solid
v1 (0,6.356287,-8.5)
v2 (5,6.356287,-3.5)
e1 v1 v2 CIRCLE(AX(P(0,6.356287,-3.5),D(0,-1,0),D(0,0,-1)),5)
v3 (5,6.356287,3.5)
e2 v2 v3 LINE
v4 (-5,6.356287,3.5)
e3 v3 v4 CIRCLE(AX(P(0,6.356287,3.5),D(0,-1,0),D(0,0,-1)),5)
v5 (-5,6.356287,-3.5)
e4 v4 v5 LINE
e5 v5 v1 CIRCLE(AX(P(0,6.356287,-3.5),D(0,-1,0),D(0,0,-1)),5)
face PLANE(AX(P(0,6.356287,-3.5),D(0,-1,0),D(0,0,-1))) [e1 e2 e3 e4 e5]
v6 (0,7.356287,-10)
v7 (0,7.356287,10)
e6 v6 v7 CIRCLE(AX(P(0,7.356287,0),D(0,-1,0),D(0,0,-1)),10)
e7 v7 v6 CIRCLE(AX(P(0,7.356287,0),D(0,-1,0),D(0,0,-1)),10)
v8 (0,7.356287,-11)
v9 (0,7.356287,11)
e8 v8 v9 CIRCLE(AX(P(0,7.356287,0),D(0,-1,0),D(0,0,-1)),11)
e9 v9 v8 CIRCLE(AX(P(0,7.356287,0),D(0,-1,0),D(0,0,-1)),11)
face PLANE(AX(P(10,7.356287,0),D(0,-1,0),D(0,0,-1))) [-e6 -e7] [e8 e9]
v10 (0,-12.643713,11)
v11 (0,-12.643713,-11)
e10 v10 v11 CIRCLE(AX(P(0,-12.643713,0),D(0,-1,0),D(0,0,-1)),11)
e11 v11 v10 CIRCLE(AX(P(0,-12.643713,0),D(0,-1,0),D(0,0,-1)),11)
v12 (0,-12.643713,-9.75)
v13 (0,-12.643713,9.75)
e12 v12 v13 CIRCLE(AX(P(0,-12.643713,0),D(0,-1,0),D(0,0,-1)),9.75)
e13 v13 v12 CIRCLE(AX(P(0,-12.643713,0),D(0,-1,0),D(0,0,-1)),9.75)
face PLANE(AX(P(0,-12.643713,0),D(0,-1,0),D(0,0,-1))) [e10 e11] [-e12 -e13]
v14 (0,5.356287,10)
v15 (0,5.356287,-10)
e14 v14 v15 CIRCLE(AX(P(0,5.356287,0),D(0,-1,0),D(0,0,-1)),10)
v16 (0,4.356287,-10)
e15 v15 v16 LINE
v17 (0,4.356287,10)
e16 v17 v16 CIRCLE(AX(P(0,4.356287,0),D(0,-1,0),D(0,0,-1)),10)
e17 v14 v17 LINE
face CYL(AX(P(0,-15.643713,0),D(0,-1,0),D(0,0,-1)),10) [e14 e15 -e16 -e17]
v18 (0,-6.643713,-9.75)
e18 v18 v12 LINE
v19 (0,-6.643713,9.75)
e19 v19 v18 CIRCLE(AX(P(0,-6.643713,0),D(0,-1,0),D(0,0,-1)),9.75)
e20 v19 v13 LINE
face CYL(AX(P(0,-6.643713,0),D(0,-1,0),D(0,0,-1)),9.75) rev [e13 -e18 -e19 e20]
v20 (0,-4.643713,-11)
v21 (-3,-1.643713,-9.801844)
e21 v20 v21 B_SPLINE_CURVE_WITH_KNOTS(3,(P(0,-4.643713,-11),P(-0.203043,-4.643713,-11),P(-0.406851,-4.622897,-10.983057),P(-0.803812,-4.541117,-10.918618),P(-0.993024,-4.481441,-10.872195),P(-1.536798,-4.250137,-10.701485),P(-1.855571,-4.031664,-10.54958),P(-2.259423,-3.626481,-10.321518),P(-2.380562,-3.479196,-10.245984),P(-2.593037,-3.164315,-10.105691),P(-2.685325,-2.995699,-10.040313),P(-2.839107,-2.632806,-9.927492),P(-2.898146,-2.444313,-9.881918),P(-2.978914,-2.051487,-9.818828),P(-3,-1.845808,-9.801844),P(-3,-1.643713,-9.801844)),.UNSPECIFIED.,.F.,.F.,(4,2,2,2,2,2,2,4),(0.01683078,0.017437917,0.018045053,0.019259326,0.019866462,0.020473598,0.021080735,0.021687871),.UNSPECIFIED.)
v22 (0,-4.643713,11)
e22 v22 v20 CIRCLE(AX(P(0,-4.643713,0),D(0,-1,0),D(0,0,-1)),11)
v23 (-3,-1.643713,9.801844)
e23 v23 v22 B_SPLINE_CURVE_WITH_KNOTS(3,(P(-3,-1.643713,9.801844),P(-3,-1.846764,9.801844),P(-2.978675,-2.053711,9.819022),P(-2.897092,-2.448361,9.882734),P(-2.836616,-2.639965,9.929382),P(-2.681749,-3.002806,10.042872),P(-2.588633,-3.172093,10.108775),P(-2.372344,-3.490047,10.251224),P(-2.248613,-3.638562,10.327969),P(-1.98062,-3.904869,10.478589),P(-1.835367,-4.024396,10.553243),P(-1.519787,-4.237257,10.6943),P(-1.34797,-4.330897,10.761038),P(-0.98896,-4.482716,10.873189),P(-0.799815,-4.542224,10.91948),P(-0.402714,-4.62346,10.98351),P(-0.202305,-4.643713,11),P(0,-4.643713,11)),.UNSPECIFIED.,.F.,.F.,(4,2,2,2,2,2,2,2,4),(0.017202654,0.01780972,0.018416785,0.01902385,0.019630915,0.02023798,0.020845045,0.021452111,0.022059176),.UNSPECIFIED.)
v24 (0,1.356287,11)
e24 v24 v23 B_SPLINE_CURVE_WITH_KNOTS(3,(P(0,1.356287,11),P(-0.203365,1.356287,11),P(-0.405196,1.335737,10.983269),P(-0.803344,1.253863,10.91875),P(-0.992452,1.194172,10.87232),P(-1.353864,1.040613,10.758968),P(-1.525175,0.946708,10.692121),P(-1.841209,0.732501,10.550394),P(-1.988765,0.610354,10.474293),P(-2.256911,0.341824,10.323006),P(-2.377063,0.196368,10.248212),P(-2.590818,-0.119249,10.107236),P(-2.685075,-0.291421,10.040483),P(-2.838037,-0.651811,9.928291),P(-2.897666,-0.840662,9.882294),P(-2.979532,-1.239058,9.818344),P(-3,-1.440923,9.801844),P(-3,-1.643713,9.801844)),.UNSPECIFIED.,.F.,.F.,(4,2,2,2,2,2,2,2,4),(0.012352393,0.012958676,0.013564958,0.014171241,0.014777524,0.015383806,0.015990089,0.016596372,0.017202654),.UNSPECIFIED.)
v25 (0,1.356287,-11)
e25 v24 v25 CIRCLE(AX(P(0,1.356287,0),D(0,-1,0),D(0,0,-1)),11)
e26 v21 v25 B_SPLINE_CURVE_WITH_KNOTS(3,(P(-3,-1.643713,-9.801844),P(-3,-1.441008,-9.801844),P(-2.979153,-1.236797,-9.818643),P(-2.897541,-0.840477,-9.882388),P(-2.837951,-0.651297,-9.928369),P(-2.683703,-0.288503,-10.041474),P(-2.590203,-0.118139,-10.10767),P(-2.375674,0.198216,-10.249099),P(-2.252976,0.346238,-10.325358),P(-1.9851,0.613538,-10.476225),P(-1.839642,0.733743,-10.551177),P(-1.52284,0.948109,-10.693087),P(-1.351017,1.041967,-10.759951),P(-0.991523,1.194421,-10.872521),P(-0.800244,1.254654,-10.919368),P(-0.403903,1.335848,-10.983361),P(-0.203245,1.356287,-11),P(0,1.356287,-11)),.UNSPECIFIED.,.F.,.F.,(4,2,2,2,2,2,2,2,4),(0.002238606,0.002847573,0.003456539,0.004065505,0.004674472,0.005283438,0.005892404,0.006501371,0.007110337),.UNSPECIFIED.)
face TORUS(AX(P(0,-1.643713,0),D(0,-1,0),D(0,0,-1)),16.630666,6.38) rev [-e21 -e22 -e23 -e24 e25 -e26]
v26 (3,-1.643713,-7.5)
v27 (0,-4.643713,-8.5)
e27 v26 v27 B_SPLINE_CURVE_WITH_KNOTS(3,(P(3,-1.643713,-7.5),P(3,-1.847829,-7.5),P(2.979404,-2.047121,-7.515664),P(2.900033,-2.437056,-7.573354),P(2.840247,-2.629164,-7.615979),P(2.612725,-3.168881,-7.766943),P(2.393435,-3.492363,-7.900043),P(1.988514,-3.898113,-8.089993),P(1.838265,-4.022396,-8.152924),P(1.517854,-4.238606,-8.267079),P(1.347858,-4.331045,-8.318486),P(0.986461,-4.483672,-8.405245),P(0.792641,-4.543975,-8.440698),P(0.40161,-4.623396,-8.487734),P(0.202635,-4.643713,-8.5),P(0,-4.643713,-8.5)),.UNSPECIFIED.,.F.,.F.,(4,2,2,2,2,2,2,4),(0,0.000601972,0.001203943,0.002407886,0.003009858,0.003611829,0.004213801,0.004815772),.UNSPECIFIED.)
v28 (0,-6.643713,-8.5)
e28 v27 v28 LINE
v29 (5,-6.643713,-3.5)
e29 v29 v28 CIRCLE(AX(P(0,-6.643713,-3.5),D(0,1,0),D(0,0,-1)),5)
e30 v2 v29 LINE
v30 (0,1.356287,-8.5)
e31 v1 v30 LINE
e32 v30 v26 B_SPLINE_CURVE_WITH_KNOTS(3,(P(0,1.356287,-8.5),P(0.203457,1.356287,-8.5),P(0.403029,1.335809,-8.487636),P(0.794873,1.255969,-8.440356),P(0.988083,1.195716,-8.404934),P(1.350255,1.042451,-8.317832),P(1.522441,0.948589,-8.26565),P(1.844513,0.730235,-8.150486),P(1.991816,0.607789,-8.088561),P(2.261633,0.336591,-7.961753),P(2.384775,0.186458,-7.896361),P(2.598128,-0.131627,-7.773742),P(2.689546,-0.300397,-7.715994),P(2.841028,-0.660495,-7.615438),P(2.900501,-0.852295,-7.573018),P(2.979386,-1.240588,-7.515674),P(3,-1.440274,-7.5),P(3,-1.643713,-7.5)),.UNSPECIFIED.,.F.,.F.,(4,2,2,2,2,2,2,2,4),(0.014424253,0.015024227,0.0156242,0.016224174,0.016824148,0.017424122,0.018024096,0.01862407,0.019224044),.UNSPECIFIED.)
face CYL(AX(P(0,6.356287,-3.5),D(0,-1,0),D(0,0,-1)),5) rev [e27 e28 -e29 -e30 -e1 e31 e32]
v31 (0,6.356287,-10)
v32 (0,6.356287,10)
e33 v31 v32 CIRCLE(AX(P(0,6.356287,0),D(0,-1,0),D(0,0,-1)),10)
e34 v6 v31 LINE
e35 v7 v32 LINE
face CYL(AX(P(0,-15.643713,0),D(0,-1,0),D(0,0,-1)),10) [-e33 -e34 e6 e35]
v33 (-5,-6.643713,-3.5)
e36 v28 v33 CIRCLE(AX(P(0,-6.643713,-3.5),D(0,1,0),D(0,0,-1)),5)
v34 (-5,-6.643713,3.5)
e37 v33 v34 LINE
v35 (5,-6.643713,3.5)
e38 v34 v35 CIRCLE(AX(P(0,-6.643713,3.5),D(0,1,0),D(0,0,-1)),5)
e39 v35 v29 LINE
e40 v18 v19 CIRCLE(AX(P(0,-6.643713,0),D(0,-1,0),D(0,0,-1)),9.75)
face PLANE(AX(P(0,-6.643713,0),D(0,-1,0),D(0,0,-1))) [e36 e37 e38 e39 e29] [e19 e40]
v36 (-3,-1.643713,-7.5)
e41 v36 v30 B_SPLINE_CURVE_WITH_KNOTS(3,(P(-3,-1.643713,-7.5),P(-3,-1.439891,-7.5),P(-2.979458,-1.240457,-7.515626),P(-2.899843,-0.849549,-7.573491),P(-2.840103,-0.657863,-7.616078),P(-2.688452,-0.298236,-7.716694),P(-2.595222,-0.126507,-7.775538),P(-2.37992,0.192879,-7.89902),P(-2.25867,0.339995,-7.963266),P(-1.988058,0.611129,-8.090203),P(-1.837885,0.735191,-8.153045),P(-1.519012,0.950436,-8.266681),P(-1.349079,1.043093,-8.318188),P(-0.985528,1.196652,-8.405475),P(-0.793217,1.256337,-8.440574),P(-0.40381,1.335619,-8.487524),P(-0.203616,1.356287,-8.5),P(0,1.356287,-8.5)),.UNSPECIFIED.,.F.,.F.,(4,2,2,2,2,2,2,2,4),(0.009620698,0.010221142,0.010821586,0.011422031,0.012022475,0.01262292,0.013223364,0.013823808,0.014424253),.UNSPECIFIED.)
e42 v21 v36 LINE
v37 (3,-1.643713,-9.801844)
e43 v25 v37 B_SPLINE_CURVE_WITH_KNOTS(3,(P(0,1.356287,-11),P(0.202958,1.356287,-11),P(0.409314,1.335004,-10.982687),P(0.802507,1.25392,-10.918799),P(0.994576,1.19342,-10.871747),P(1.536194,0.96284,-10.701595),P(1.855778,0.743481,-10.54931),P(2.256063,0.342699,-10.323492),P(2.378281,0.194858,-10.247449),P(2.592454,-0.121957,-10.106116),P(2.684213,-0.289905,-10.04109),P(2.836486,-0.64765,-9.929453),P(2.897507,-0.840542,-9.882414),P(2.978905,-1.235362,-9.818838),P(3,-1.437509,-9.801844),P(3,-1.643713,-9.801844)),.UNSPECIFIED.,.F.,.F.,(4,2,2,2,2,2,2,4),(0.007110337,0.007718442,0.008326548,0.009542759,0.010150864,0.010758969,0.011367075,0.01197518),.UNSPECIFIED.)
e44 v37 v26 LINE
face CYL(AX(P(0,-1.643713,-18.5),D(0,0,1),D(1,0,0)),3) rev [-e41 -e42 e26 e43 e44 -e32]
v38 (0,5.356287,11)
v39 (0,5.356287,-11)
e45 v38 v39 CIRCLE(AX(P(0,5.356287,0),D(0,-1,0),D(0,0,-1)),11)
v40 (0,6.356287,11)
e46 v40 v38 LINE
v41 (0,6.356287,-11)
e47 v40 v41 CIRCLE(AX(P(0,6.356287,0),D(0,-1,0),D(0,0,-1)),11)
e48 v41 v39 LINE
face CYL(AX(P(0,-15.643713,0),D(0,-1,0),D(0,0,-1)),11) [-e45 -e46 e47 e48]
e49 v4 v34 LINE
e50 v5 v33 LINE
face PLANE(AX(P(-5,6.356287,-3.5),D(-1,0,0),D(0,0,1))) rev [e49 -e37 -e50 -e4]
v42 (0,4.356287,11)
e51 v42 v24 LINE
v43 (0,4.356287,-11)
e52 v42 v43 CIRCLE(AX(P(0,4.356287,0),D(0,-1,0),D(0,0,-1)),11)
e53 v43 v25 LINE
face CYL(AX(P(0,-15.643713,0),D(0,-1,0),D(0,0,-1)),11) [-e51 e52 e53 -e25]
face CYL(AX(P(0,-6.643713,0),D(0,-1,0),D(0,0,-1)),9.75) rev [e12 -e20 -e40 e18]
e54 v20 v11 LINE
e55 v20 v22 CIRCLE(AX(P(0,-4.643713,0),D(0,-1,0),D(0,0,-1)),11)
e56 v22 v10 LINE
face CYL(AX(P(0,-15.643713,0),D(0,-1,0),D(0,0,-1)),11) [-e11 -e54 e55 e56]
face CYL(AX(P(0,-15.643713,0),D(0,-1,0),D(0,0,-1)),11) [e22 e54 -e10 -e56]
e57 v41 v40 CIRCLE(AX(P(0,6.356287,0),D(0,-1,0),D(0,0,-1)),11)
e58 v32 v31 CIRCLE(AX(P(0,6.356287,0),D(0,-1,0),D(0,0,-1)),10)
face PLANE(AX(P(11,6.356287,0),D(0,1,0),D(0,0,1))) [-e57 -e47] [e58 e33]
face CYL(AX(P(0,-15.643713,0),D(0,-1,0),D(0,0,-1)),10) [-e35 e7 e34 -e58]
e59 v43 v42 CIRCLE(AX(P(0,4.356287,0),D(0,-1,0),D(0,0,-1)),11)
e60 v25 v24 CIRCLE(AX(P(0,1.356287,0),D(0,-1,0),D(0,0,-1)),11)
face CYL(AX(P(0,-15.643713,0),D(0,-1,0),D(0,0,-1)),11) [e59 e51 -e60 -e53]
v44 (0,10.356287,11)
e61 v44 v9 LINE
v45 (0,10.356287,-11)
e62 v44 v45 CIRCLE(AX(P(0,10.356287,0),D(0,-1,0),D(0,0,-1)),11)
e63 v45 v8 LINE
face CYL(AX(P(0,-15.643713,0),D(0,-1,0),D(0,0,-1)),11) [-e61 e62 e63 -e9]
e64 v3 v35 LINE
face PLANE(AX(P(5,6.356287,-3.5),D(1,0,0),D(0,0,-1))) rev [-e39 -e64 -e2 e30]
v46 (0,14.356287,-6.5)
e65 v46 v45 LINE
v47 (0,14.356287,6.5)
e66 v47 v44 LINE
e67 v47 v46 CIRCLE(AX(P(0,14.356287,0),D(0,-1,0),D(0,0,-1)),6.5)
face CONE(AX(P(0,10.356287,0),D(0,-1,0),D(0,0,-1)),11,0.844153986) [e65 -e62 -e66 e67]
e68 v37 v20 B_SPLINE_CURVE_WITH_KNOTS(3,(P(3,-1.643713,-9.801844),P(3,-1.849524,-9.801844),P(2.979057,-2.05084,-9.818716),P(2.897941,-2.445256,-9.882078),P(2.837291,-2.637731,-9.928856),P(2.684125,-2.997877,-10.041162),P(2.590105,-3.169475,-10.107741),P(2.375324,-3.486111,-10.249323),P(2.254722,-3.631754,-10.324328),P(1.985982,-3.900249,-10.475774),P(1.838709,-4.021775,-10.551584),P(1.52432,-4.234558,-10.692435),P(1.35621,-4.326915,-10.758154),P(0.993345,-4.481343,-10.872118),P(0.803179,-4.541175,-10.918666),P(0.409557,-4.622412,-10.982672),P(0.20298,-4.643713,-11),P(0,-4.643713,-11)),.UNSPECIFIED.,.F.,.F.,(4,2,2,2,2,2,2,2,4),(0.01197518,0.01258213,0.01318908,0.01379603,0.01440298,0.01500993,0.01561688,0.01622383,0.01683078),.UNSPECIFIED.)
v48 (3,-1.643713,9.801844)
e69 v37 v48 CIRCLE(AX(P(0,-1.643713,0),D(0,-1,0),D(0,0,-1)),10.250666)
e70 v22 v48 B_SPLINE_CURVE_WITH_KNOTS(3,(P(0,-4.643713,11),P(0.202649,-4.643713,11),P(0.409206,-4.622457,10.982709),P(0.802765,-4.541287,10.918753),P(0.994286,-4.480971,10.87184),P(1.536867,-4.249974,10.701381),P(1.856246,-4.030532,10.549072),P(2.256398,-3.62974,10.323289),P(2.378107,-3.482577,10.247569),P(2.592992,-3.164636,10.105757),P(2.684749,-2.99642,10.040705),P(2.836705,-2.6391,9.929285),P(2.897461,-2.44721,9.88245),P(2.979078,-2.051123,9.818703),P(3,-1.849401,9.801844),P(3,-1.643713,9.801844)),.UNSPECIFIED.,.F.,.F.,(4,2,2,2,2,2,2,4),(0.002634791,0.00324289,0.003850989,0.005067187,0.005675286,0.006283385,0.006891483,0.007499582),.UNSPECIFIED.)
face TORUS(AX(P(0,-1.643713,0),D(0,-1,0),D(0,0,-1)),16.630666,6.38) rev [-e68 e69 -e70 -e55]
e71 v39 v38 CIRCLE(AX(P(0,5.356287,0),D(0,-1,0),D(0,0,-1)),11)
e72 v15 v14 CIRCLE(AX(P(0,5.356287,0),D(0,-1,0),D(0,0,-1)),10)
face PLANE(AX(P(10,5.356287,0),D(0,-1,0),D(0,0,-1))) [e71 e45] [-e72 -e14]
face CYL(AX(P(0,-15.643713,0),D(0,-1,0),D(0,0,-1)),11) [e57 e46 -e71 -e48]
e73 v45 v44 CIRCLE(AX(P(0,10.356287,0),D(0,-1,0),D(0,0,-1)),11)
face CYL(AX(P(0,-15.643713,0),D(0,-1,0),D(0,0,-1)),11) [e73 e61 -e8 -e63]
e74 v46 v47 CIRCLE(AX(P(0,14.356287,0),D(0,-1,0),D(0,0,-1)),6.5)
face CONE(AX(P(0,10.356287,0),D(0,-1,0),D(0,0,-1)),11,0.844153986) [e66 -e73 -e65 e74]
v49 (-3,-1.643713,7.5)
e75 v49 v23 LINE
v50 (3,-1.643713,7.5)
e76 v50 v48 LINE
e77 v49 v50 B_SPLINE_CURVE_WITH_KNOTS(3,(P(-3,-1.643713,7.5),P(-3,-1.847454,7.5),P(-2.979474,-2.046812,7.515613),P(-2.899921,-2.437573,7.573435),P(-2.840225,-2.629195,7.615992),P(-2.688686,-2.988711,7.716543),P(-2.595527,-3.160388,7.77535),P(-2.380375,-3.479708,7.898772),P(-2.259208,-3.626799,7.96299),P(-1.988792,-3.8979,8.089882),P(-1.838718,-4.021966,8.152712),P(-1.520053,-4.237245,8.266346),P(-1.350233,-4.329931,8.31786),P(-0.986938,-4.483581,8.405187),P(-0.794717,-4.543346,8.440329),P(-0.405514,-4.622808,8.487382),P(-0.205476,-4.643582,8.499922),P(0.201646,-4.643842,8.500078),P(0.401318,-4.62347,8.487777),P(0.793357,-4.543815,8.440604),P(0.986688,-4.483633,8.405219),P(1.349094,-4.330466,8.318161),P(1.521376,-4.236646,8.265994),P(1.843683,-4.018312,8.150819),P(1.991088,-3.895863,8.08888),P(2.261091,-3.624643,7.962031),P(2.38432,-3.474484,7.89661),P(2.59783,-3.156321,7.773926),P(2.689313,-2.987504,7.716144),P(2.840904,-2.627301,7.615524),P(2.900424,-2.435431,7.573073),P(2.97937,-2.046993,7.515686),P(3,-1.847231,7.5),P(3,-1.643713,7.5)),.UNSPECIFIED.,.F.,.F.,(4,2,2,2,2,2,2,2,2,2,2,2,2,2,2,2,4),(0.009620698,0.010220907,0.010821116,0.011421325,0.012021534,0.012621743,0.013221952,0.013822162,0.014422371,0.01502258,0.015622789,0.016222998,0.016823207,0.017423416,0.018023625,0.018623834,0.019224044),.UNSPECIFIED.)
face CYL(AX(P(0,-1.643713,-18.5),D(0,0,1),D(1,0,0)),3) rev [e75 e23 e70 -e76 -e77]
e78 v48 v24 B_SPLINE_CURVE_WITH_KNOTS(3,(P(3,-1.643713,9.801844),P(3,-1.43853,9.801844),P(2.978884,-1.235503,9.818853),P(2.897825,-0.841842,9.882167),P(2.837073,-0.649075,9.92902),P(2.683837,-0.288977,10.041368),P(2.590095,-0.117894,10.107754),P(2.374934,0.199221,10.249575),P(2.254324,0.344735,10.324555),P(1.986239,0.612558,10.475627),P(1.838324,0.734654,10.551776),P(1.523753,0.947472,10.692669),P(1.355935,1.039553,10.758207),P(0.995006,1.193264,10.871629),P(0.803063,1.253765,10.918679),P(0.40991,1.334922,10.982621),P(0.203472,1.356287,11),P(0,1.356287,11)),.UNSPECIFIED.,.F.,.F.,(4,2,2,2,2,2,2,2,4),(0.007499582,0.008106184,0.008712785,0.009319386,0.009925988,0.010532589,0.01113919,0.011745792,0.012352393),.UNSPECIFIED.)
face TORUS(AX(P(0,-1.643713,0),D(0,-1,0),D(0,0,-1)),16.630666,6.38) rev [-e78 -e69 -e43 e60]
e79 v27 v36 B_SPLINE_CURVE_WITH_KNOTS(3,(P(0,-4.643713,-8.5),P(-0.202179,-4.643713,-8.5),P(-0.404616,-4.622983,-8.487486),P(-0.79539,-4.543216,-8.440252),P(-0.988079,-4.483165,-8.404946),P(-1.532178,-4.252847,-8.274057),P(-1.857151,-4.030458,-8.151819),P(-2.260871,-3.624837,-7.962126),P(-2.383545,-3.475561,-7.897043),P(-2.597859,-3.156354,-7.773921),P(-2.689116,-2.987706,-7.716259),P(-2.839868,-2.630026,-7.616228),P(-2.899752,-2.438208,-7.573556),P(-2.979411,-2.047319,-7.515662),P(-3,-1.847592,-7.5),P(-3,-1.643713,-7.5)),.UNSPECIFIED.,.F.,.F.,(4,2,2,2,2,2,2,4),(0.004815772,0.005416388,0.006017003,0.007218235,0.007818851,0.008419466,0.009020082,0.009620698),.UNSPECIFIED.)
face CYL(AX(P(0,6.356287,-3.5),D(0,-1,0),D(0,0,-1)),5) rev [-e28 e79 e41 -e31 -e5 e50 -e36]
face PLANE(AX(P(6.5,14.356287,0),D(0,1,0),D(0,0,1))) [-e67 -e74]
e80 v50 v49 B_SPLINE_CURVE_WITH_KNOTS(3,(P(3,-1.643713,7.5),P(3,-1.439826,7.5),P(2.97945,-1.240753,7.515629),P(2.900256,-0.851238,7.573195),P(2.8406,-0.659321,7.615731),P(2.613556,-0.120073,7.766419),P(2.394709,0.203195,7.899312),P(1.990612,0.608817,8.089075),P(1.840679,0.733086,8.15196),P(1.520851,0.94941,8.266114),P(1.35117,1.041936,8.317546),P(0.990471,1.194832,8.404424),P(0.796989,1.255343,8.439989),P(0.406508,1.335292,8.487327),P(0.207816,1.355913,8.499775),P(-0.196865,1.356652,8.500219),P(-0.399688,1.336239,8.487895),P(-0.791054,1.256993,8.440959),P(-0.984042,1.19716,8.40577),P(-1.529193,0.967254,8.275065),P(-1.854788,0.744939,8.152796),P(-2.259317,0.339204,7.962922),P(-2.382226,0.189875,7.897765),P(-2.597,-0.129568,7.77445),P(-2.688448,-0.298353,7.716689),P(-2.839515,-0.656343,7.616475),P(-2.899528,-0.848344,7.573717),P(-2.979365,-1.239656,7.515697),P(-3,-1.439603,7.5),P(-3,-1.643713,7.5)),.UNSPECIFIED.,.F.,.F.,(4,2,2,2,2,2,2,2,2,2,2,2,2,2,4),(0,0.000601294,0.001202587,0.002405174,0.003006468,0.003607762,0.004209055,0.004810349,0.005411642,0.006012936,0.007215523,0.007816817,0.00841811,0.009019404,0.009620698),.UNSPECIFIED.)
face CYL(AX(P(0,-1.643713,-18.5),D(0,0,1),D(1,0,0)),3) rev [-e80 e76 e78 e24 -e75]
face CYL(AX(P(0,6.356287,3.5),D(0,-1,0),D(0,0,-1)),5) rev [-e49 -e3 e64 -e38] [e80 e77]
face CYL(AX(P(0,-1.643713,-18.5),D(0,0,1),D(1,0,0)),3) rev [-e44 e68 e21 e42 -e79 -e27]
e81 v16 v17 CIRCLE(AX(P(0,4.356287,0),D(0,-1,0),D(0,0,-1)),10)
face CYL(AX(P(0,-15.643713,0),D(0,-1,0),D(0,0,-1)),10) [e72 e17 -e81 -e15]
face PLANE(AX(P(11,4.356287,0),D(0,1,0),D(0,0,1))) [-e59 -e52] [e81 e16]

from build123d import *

# Parameters (mm, degrees)
CON_ROD_SLOT_DEPTH        = 19
UNDERSIDE_BORE_SKETCH_R   = 9.75
UNDERSIDE_BORE_19_5_DEPTH = 6
WRIST_PIN_HOLE_SKETCH_R   = 3
WRIST_PIN_HOLE_6_DEPTH    = 18.500000000000004


with BuildPart() as part:
    # Piston Profile Sketch → Piston Body (revolve)
    with BuildSketch(Plane.XY, mode=Mode.PRIVATE) as piston_body_sk:
        with BuildLine():
            Line((0, -12.6437125748503), (11.000000000000002, -12.6437125748503))
            Line((11.000000000000002, -12.6437125748503), (11.000000000000002, -4.643712574850299))
            ThreePointArc((11.000000000000002, -4.643712574850299), (10.250666035204008, -1.6437125748502983), (11.000000000000002, 1.3562874251497004))
            Line((11.000000000000002, 1.3562874251497004), (11.000000000000002, 4.356287425149702))
            Line((11.000000000000002, 4.356287425149702), (10.000000000000002, 4.356287425149703))
            Line((10.000000000000002, 4.356287425149703), (10.000000000000002, 5.3562874251496995))
            Line((10.000000000000002, 5.3562874251496995), (11, 5.3562874251496995))
            Line((11, 5.3562874251496995), (11, 6.3562874251497))
            Line((11, 6.3562874251497), (10.000000000000002, 6.356287425149702))
            Line((10.000000000000002, 6.356287425149702), (10.000000000000002, 7.356287425149701))
            Line((10.000000000000002, 7.356287425149701), (11.000000000000002, 7.356287425149701))
            Line((11.000000000000002, 7.356287425149701), (11.000000000000002, 10.356287425149699))
            Line((11.000000000000002, 10.356287425149699), (6.5, 14.356287425149699))
            Line((6.5, 14.356287425149699), (-1.8e-16, 14.356287425149699))
            Line((-1.8e-16, 14.356287425149699), (0, -12.6437125748503))
        make_face()
    revolve(piston_body_sk.sketch.rotate(Axis((0, -15.6437125748503, 0), (0, 1, 0)), 90), axis=Axis((0, -15.6437125748503, 0), (0, 1, 0)))

    # Con Rod Slot Sketch → Con Rod Slot (cut)
    with BuildSketch(Plane.XZ.offset(12.6437125748503)):
        with BuildLine():
            Line((-4.999999999999999, -3.5000000000000013), (-5.000000000000002, 3.499999999999997))
            ThreePointArc((-5.000000000000002, 3.499999999999997), (-3.54e-15, 8.500000000000002), (5, 3.500000000000003))
            Line((5, 3.500000000000003), (5.000000000000003, -3.4999999999999987))
            ThreePointArc((5.000000000000003, -3.4999999999999987), (2.79e-15, -8.5), (-4.999999999999999, -3.5000000000000013))
        make_face()
    extrude(amount=-CON_ROD_SLOT_DEPTH, mode=Mode.SUBTRACT)

    # Underside Bore Sketch → Underside Bore Ø19.5 (cut)
    with BuildSketch(Plane.XZ.offset(12.6437125748503)):
        with Locations(Location((0, 0, 0), (0, 0, 270))):
            Circle(UNDERSIDE_BORE_SKETCH_R)
    extrude(amount=-UNDERSIDE_BORE_19_5_DEPTH, mode=Mode.SUBTRACT)

    # Wrist Pin Hole Sketch → Wrist Pin Hole Ø6 (cut, symmetric)
    with BuildSketch(Plane.XY):
        with Locations((0, -1.6437125748502988)):
            Circle(WRIST_PIN_HOLE_SKETCH_R)
    extrude(amount=WRIST_PIN_HOLE_6_DEPTH, both=True, mode=Mode.SUBTRACT)


solid = part.part
